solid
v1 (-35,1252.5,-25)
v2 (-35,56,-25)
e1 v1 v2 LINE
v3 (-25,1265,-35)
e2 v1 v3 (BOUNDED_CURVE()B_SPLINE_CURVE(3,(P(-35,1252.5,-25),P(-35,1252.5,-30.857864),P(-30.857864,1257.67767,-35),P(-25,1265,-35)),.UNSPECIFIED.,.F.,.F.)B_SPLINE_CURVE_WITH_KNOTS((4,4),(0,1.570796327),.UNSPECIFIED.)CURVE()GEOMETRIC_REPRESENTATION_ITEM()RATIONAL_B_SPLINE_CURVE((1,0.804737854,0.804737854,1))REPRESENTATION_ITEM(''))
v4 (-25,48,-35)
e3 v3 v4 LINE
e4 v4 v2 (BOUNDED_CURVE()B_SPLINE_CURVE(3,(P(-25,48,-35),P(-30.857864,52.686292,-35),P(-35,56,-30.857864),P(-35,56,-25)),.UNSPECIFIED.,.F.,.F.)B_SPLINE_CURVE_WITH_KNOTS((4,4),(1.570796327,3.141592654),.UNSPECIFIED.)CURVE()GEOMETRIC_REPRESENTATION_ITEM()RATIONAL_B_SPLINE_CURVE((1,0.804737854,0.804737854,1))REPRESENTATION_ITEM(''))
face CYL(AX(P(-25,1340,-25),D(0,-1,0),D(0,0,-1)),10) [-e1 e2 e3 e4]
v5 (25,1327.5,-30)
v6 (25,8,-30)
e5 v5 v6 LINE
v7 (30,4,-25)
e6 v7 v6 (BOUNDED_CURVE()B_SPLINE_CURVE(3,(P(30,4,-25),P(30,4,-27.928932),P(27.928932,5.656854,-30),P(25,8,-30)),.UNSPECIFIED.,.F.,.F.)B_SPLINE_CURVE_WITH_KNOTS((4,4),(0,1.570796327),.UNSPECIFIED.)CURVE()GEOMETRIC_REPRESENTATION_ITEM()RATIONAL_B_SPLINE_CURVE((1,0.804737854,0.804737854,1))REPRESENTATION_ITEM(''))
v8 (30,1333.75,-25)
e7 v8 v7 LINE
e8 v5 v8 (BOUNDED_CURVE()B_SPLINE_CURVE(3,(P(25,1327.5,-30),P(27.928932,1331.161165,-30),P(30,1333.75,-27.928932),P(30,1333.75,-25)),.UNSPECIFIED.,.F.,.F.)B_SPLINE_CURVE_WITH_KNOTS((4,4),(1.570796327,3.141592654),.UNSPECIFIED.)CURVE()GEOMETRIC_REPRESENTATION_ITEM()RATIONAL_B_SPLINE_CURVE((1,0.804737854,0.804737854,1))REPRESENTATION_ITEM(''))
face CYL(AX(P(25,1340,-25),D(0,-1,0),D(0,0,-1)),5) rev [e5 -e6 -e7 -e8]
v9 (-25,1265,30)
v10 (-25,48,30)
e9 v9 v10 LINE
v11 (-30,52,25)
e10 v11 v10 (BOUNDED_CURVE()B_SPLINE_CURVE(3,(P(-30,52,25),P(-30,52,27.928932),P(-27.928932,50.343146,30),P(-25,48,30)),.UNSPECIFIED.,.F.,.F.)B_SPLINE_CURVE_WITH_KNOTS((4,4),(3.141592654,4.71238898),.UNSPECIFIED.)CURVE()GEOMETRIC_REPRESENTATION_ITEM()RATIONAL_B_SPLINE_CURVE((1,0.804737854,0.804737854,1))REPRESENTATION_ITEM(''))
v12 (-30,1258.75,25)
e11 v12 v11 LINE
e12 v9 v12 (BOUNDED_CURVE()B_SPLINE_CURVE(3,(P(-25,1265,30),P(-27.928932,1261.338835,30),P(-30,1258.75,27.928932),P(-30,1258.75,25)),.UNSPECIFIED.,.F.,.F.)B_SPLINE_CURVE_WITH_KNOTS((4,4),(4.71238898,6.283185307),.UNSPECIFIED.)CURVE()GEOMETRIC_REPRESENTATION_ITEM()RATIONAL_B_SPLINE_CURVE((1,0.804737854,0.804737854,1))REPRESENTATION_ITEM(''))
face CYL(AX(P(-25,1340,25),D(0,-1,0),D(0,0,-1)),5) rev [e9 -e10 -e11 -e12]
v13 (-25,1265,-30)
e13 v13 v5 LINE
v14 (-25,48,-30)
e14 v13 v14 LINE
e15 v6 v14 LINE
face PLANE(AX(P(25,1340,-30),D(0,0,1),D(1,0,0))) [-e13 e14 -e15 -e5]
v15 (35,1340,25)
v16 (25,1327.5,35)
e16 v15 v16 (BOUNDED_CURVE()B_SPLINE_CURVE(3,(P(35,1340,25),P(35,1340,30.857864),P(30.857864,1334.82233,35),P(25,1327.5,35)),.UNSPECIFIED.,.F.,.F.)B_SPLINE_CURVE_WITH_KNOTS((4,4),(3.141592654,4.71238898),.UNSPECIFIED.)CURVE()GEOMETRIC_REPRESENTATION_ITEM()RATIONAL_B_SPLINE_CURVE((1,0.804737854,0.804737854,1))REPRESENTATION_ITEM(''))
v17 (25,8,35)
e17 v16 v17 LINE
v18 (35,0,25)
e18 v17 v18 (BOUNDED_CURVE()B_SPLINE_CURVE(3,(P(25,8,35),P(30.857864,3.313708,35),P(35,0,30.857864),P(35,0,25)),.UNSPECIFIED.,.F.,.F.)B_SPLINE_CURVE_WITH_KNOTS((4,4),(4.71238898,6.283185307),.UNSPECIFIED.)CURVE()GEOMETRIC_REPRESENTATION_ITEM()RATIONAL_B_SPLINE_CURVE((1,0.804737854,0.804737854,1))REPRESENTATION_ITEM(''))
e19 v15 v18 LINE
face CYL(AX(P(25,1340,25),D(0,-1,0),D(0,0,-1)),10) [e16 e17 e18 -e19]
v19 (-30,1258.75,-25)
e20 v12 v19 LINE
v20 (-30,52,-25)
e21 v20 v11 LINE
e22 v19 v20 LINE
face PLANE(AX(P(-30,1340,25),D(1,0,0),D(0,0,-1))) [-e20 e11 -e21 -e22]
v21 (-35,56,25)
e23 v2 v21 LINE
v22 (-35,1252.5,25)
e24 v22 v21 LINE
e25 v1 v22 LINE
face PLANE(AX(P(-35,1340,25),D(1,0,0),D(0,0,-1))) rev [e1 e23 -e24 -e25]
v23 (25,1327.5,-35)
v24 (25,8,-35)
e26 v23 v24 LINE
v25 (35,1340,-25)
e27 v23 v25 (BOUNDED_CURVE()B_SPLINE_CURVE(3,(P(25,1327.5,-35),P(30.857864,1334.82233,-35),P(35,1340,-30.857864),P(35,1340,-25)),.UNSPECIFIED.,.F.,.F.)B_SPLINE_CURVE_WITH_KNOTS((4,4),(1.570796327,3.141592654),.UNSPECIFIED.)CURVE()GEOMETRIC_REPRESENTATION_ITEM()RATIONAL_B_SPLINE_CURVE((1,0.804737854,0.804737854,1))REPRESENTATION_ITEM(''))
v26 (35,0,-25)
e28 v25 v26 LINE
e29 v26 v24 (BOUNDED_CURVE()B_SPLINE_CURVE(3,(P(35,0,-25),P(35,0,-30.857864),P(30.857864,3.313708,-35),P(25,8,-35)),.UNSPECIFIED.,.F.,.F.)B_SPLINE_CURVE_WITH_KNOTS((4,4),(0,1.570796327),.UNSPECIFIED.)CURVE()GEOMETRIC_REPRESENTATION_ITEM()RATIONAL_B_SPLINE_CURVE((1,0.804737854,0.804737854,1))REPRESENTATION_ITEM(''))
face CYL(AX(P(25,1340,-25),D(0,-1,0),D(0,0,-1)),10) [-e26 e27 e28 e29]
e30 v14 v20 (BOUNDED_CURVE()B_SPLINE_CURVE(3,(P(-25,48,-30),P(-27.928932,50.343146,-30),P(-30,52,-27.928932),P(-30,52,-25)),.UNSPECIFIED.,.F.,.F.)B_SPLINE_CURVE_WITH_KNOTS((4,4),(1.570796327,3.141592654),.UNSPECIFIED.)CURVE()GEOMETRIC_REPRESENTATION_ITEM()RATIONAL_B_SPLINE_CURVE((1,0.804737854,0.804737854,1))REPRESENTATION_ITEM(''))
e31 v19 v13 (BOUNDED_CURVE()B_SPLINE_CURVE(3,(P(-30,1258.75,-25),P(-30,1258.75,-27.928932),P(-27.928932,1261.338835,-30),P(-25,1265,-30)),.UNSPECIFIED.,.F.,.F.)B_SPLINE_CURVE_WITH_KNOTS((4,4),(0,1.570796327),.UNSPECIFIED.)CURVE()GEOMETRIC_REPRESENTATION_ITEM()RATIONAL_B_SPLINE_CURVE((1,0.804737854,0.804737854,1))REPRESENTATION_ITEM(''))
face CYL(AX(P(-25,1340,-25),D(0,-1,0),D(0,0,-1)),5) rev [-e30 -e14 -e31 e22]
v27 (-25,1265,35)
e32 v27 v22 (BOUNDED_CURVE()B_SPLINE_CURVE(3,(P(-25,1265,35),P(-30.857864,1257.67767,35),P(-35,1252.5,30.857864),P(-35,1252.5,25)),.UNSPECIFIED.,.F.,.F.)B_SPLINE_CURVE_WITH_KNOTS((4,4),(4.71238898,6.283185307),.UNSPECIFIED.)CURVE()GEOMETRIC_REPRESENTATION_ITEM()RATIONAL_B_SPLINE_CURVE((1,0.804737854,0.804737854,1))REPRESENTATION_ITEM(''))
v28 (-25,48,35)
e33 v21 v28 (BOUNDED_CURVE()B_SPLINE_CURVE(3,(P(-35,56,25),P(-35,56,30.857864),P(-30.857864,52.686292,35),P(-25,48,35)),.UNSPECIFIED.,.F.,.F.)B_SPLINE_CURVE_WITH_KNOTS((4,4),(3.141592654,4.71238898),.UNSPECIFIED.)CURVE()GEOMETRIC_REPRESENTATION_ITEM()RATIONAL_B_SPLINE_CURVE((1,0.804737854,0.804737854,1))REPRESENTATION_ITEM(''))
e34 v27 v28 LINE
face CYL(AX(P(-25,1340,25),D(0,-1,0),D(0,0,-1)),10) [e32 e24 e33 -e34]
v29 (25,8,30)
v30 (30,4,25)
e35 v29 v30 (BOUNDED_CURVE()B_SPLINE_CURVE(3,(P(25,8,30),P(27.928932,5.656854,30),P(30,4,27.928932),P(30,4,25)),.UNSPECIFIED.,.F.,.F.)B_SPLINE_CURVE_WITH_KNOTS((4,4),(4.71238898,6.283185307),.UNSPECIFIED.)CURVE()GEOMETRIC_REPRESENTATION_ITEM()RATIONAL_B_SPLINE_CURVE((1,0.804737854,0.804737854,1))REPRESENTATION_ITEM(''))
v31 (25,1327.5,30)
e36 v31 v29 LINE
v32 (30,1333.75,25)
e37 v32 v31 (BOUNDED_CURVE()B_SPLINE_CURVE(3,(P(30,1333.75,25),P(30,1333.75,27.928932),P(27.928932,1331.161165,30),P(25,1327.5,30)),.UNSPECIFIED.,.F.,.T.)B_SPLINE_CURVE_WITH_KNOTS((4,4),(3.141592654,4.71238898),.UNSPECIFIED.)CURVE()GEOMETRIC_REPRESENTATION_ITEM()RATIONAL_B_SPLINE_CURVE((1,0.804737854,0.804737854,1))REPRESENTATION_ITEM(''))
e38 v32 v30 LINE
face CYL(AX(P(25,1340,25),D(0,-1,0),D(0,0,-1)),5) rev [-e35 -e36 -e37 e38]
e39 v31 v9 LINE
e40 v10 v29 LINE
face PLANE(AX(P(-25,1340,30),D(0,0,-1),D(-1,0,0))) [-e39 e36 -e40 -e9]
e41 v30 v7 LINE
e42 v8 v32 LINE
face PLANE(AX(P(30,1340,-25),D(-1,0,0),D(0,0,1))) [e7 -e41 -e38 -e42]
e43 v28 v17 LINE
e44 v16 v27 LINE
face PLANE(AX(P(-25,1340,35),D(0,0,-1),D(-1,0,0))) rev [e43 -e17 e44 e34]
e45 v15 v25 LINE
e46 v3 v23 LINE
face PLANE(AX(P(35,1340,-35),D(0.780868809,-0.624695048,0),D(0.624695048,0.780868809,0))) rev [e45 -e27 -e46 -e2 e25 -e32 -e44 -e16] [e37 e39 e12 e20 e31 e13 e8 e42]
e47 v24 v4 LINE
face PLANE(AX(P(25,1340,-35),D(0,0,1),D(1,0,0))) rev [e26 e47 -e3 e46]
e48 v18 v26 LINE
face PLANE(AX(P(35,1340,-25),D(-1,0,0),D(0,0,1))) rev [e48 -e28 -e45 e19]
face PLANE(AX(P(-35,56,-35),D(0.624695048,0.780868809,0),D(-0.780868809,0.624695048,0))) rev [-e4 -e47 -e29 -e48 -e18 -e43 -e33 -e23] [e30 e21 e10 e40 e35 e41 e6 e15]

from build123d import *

# Parameters (mm, degrees)
F_19_WELDMEMBERFEAT_4_MORE_IN_5_FILES_DEPTH = 1340
CUT_EXTRUDE1_DEPTH                          = 1343.283502096
CUT_EXTRUDE1_DEPTH_BACK                     = 1343.283502096


with BuildPart() as part:
    # Sketch1 → 19 (WeldMemberFeat) (+4 more in 5 files) Cold-formed hollow square steel (GB/T 6728-2002) 70×70×5(1) (new body)
    with BuildSketch(Plane(origin=(0, 0, 0), x_dir=(-1, 0, 0), z_dir=(0, 1, 0))):
        with BuildLine():
            Line((-25, -35), (25, -35))
            ThreePointArc((25, -35), (32.071067812, -32.071067812), (35, -25))
            Line((35, -25), (35, 25))
            ThreePointArc((35, 25), (32.071067812, 32.071067812), (25, 35))
            Line((25, 35), (-25, 35))
            ThreePointArc((-25, 35), (-32.071067812, 32.071067812), (-35, 25))
            Line((-35, 25), (-35, -25))
            ThreePointArc((-35, -25), (-32.071067812, -32.071067812), (-25, -35))
        make_face()
        with BuildLine():
            Line((-25, -30), (25, -30))
            ThreePointArc((25, -30), (28.535533906, -28.535533906), (30, -25))
            Line((30, -25), (30, 25))
            ThreePointArc((30, 25), (28.535533906, 28.535533906), (25, 30))
            Line((25, 30), (-25, 30))
            ThreePointArc((-25, 30), (-28.535533906, 28.535533906), (-30, 25))
            Line((-30, 25), (-30, -25))
            ThreePointArc((-30, -25), (-28.535533906, -28.535533906), (-25, -30))
        make_face(mode=Mode.SUBTRACT)
    extrude(amount=F_19_WELDMEMBERFEAT_4_MORE_IN_5_FILES_DEPTH)

    # Sketch2 → Cut-Extrude1 (cut, two sides: drawn at the far end of the back side and taken through both)
    with BuildSketch(Plane.XY.offset(35).offset(-CUT_EXTRUDE1_DEPTH_BACK)):
        Polygon((35, 1340), (-35, 1252.5), (-35, 1340), align=None)
        Polygon((-35, 56), (35, 0), (-35, 0), align=None)
    extrude(amount=CUT_EXTRUDE1_DEPTH + CUT_EXTRUDE1_DEPTH_BACK, mode=Mode.SUBTRACT)


solid = part.part
